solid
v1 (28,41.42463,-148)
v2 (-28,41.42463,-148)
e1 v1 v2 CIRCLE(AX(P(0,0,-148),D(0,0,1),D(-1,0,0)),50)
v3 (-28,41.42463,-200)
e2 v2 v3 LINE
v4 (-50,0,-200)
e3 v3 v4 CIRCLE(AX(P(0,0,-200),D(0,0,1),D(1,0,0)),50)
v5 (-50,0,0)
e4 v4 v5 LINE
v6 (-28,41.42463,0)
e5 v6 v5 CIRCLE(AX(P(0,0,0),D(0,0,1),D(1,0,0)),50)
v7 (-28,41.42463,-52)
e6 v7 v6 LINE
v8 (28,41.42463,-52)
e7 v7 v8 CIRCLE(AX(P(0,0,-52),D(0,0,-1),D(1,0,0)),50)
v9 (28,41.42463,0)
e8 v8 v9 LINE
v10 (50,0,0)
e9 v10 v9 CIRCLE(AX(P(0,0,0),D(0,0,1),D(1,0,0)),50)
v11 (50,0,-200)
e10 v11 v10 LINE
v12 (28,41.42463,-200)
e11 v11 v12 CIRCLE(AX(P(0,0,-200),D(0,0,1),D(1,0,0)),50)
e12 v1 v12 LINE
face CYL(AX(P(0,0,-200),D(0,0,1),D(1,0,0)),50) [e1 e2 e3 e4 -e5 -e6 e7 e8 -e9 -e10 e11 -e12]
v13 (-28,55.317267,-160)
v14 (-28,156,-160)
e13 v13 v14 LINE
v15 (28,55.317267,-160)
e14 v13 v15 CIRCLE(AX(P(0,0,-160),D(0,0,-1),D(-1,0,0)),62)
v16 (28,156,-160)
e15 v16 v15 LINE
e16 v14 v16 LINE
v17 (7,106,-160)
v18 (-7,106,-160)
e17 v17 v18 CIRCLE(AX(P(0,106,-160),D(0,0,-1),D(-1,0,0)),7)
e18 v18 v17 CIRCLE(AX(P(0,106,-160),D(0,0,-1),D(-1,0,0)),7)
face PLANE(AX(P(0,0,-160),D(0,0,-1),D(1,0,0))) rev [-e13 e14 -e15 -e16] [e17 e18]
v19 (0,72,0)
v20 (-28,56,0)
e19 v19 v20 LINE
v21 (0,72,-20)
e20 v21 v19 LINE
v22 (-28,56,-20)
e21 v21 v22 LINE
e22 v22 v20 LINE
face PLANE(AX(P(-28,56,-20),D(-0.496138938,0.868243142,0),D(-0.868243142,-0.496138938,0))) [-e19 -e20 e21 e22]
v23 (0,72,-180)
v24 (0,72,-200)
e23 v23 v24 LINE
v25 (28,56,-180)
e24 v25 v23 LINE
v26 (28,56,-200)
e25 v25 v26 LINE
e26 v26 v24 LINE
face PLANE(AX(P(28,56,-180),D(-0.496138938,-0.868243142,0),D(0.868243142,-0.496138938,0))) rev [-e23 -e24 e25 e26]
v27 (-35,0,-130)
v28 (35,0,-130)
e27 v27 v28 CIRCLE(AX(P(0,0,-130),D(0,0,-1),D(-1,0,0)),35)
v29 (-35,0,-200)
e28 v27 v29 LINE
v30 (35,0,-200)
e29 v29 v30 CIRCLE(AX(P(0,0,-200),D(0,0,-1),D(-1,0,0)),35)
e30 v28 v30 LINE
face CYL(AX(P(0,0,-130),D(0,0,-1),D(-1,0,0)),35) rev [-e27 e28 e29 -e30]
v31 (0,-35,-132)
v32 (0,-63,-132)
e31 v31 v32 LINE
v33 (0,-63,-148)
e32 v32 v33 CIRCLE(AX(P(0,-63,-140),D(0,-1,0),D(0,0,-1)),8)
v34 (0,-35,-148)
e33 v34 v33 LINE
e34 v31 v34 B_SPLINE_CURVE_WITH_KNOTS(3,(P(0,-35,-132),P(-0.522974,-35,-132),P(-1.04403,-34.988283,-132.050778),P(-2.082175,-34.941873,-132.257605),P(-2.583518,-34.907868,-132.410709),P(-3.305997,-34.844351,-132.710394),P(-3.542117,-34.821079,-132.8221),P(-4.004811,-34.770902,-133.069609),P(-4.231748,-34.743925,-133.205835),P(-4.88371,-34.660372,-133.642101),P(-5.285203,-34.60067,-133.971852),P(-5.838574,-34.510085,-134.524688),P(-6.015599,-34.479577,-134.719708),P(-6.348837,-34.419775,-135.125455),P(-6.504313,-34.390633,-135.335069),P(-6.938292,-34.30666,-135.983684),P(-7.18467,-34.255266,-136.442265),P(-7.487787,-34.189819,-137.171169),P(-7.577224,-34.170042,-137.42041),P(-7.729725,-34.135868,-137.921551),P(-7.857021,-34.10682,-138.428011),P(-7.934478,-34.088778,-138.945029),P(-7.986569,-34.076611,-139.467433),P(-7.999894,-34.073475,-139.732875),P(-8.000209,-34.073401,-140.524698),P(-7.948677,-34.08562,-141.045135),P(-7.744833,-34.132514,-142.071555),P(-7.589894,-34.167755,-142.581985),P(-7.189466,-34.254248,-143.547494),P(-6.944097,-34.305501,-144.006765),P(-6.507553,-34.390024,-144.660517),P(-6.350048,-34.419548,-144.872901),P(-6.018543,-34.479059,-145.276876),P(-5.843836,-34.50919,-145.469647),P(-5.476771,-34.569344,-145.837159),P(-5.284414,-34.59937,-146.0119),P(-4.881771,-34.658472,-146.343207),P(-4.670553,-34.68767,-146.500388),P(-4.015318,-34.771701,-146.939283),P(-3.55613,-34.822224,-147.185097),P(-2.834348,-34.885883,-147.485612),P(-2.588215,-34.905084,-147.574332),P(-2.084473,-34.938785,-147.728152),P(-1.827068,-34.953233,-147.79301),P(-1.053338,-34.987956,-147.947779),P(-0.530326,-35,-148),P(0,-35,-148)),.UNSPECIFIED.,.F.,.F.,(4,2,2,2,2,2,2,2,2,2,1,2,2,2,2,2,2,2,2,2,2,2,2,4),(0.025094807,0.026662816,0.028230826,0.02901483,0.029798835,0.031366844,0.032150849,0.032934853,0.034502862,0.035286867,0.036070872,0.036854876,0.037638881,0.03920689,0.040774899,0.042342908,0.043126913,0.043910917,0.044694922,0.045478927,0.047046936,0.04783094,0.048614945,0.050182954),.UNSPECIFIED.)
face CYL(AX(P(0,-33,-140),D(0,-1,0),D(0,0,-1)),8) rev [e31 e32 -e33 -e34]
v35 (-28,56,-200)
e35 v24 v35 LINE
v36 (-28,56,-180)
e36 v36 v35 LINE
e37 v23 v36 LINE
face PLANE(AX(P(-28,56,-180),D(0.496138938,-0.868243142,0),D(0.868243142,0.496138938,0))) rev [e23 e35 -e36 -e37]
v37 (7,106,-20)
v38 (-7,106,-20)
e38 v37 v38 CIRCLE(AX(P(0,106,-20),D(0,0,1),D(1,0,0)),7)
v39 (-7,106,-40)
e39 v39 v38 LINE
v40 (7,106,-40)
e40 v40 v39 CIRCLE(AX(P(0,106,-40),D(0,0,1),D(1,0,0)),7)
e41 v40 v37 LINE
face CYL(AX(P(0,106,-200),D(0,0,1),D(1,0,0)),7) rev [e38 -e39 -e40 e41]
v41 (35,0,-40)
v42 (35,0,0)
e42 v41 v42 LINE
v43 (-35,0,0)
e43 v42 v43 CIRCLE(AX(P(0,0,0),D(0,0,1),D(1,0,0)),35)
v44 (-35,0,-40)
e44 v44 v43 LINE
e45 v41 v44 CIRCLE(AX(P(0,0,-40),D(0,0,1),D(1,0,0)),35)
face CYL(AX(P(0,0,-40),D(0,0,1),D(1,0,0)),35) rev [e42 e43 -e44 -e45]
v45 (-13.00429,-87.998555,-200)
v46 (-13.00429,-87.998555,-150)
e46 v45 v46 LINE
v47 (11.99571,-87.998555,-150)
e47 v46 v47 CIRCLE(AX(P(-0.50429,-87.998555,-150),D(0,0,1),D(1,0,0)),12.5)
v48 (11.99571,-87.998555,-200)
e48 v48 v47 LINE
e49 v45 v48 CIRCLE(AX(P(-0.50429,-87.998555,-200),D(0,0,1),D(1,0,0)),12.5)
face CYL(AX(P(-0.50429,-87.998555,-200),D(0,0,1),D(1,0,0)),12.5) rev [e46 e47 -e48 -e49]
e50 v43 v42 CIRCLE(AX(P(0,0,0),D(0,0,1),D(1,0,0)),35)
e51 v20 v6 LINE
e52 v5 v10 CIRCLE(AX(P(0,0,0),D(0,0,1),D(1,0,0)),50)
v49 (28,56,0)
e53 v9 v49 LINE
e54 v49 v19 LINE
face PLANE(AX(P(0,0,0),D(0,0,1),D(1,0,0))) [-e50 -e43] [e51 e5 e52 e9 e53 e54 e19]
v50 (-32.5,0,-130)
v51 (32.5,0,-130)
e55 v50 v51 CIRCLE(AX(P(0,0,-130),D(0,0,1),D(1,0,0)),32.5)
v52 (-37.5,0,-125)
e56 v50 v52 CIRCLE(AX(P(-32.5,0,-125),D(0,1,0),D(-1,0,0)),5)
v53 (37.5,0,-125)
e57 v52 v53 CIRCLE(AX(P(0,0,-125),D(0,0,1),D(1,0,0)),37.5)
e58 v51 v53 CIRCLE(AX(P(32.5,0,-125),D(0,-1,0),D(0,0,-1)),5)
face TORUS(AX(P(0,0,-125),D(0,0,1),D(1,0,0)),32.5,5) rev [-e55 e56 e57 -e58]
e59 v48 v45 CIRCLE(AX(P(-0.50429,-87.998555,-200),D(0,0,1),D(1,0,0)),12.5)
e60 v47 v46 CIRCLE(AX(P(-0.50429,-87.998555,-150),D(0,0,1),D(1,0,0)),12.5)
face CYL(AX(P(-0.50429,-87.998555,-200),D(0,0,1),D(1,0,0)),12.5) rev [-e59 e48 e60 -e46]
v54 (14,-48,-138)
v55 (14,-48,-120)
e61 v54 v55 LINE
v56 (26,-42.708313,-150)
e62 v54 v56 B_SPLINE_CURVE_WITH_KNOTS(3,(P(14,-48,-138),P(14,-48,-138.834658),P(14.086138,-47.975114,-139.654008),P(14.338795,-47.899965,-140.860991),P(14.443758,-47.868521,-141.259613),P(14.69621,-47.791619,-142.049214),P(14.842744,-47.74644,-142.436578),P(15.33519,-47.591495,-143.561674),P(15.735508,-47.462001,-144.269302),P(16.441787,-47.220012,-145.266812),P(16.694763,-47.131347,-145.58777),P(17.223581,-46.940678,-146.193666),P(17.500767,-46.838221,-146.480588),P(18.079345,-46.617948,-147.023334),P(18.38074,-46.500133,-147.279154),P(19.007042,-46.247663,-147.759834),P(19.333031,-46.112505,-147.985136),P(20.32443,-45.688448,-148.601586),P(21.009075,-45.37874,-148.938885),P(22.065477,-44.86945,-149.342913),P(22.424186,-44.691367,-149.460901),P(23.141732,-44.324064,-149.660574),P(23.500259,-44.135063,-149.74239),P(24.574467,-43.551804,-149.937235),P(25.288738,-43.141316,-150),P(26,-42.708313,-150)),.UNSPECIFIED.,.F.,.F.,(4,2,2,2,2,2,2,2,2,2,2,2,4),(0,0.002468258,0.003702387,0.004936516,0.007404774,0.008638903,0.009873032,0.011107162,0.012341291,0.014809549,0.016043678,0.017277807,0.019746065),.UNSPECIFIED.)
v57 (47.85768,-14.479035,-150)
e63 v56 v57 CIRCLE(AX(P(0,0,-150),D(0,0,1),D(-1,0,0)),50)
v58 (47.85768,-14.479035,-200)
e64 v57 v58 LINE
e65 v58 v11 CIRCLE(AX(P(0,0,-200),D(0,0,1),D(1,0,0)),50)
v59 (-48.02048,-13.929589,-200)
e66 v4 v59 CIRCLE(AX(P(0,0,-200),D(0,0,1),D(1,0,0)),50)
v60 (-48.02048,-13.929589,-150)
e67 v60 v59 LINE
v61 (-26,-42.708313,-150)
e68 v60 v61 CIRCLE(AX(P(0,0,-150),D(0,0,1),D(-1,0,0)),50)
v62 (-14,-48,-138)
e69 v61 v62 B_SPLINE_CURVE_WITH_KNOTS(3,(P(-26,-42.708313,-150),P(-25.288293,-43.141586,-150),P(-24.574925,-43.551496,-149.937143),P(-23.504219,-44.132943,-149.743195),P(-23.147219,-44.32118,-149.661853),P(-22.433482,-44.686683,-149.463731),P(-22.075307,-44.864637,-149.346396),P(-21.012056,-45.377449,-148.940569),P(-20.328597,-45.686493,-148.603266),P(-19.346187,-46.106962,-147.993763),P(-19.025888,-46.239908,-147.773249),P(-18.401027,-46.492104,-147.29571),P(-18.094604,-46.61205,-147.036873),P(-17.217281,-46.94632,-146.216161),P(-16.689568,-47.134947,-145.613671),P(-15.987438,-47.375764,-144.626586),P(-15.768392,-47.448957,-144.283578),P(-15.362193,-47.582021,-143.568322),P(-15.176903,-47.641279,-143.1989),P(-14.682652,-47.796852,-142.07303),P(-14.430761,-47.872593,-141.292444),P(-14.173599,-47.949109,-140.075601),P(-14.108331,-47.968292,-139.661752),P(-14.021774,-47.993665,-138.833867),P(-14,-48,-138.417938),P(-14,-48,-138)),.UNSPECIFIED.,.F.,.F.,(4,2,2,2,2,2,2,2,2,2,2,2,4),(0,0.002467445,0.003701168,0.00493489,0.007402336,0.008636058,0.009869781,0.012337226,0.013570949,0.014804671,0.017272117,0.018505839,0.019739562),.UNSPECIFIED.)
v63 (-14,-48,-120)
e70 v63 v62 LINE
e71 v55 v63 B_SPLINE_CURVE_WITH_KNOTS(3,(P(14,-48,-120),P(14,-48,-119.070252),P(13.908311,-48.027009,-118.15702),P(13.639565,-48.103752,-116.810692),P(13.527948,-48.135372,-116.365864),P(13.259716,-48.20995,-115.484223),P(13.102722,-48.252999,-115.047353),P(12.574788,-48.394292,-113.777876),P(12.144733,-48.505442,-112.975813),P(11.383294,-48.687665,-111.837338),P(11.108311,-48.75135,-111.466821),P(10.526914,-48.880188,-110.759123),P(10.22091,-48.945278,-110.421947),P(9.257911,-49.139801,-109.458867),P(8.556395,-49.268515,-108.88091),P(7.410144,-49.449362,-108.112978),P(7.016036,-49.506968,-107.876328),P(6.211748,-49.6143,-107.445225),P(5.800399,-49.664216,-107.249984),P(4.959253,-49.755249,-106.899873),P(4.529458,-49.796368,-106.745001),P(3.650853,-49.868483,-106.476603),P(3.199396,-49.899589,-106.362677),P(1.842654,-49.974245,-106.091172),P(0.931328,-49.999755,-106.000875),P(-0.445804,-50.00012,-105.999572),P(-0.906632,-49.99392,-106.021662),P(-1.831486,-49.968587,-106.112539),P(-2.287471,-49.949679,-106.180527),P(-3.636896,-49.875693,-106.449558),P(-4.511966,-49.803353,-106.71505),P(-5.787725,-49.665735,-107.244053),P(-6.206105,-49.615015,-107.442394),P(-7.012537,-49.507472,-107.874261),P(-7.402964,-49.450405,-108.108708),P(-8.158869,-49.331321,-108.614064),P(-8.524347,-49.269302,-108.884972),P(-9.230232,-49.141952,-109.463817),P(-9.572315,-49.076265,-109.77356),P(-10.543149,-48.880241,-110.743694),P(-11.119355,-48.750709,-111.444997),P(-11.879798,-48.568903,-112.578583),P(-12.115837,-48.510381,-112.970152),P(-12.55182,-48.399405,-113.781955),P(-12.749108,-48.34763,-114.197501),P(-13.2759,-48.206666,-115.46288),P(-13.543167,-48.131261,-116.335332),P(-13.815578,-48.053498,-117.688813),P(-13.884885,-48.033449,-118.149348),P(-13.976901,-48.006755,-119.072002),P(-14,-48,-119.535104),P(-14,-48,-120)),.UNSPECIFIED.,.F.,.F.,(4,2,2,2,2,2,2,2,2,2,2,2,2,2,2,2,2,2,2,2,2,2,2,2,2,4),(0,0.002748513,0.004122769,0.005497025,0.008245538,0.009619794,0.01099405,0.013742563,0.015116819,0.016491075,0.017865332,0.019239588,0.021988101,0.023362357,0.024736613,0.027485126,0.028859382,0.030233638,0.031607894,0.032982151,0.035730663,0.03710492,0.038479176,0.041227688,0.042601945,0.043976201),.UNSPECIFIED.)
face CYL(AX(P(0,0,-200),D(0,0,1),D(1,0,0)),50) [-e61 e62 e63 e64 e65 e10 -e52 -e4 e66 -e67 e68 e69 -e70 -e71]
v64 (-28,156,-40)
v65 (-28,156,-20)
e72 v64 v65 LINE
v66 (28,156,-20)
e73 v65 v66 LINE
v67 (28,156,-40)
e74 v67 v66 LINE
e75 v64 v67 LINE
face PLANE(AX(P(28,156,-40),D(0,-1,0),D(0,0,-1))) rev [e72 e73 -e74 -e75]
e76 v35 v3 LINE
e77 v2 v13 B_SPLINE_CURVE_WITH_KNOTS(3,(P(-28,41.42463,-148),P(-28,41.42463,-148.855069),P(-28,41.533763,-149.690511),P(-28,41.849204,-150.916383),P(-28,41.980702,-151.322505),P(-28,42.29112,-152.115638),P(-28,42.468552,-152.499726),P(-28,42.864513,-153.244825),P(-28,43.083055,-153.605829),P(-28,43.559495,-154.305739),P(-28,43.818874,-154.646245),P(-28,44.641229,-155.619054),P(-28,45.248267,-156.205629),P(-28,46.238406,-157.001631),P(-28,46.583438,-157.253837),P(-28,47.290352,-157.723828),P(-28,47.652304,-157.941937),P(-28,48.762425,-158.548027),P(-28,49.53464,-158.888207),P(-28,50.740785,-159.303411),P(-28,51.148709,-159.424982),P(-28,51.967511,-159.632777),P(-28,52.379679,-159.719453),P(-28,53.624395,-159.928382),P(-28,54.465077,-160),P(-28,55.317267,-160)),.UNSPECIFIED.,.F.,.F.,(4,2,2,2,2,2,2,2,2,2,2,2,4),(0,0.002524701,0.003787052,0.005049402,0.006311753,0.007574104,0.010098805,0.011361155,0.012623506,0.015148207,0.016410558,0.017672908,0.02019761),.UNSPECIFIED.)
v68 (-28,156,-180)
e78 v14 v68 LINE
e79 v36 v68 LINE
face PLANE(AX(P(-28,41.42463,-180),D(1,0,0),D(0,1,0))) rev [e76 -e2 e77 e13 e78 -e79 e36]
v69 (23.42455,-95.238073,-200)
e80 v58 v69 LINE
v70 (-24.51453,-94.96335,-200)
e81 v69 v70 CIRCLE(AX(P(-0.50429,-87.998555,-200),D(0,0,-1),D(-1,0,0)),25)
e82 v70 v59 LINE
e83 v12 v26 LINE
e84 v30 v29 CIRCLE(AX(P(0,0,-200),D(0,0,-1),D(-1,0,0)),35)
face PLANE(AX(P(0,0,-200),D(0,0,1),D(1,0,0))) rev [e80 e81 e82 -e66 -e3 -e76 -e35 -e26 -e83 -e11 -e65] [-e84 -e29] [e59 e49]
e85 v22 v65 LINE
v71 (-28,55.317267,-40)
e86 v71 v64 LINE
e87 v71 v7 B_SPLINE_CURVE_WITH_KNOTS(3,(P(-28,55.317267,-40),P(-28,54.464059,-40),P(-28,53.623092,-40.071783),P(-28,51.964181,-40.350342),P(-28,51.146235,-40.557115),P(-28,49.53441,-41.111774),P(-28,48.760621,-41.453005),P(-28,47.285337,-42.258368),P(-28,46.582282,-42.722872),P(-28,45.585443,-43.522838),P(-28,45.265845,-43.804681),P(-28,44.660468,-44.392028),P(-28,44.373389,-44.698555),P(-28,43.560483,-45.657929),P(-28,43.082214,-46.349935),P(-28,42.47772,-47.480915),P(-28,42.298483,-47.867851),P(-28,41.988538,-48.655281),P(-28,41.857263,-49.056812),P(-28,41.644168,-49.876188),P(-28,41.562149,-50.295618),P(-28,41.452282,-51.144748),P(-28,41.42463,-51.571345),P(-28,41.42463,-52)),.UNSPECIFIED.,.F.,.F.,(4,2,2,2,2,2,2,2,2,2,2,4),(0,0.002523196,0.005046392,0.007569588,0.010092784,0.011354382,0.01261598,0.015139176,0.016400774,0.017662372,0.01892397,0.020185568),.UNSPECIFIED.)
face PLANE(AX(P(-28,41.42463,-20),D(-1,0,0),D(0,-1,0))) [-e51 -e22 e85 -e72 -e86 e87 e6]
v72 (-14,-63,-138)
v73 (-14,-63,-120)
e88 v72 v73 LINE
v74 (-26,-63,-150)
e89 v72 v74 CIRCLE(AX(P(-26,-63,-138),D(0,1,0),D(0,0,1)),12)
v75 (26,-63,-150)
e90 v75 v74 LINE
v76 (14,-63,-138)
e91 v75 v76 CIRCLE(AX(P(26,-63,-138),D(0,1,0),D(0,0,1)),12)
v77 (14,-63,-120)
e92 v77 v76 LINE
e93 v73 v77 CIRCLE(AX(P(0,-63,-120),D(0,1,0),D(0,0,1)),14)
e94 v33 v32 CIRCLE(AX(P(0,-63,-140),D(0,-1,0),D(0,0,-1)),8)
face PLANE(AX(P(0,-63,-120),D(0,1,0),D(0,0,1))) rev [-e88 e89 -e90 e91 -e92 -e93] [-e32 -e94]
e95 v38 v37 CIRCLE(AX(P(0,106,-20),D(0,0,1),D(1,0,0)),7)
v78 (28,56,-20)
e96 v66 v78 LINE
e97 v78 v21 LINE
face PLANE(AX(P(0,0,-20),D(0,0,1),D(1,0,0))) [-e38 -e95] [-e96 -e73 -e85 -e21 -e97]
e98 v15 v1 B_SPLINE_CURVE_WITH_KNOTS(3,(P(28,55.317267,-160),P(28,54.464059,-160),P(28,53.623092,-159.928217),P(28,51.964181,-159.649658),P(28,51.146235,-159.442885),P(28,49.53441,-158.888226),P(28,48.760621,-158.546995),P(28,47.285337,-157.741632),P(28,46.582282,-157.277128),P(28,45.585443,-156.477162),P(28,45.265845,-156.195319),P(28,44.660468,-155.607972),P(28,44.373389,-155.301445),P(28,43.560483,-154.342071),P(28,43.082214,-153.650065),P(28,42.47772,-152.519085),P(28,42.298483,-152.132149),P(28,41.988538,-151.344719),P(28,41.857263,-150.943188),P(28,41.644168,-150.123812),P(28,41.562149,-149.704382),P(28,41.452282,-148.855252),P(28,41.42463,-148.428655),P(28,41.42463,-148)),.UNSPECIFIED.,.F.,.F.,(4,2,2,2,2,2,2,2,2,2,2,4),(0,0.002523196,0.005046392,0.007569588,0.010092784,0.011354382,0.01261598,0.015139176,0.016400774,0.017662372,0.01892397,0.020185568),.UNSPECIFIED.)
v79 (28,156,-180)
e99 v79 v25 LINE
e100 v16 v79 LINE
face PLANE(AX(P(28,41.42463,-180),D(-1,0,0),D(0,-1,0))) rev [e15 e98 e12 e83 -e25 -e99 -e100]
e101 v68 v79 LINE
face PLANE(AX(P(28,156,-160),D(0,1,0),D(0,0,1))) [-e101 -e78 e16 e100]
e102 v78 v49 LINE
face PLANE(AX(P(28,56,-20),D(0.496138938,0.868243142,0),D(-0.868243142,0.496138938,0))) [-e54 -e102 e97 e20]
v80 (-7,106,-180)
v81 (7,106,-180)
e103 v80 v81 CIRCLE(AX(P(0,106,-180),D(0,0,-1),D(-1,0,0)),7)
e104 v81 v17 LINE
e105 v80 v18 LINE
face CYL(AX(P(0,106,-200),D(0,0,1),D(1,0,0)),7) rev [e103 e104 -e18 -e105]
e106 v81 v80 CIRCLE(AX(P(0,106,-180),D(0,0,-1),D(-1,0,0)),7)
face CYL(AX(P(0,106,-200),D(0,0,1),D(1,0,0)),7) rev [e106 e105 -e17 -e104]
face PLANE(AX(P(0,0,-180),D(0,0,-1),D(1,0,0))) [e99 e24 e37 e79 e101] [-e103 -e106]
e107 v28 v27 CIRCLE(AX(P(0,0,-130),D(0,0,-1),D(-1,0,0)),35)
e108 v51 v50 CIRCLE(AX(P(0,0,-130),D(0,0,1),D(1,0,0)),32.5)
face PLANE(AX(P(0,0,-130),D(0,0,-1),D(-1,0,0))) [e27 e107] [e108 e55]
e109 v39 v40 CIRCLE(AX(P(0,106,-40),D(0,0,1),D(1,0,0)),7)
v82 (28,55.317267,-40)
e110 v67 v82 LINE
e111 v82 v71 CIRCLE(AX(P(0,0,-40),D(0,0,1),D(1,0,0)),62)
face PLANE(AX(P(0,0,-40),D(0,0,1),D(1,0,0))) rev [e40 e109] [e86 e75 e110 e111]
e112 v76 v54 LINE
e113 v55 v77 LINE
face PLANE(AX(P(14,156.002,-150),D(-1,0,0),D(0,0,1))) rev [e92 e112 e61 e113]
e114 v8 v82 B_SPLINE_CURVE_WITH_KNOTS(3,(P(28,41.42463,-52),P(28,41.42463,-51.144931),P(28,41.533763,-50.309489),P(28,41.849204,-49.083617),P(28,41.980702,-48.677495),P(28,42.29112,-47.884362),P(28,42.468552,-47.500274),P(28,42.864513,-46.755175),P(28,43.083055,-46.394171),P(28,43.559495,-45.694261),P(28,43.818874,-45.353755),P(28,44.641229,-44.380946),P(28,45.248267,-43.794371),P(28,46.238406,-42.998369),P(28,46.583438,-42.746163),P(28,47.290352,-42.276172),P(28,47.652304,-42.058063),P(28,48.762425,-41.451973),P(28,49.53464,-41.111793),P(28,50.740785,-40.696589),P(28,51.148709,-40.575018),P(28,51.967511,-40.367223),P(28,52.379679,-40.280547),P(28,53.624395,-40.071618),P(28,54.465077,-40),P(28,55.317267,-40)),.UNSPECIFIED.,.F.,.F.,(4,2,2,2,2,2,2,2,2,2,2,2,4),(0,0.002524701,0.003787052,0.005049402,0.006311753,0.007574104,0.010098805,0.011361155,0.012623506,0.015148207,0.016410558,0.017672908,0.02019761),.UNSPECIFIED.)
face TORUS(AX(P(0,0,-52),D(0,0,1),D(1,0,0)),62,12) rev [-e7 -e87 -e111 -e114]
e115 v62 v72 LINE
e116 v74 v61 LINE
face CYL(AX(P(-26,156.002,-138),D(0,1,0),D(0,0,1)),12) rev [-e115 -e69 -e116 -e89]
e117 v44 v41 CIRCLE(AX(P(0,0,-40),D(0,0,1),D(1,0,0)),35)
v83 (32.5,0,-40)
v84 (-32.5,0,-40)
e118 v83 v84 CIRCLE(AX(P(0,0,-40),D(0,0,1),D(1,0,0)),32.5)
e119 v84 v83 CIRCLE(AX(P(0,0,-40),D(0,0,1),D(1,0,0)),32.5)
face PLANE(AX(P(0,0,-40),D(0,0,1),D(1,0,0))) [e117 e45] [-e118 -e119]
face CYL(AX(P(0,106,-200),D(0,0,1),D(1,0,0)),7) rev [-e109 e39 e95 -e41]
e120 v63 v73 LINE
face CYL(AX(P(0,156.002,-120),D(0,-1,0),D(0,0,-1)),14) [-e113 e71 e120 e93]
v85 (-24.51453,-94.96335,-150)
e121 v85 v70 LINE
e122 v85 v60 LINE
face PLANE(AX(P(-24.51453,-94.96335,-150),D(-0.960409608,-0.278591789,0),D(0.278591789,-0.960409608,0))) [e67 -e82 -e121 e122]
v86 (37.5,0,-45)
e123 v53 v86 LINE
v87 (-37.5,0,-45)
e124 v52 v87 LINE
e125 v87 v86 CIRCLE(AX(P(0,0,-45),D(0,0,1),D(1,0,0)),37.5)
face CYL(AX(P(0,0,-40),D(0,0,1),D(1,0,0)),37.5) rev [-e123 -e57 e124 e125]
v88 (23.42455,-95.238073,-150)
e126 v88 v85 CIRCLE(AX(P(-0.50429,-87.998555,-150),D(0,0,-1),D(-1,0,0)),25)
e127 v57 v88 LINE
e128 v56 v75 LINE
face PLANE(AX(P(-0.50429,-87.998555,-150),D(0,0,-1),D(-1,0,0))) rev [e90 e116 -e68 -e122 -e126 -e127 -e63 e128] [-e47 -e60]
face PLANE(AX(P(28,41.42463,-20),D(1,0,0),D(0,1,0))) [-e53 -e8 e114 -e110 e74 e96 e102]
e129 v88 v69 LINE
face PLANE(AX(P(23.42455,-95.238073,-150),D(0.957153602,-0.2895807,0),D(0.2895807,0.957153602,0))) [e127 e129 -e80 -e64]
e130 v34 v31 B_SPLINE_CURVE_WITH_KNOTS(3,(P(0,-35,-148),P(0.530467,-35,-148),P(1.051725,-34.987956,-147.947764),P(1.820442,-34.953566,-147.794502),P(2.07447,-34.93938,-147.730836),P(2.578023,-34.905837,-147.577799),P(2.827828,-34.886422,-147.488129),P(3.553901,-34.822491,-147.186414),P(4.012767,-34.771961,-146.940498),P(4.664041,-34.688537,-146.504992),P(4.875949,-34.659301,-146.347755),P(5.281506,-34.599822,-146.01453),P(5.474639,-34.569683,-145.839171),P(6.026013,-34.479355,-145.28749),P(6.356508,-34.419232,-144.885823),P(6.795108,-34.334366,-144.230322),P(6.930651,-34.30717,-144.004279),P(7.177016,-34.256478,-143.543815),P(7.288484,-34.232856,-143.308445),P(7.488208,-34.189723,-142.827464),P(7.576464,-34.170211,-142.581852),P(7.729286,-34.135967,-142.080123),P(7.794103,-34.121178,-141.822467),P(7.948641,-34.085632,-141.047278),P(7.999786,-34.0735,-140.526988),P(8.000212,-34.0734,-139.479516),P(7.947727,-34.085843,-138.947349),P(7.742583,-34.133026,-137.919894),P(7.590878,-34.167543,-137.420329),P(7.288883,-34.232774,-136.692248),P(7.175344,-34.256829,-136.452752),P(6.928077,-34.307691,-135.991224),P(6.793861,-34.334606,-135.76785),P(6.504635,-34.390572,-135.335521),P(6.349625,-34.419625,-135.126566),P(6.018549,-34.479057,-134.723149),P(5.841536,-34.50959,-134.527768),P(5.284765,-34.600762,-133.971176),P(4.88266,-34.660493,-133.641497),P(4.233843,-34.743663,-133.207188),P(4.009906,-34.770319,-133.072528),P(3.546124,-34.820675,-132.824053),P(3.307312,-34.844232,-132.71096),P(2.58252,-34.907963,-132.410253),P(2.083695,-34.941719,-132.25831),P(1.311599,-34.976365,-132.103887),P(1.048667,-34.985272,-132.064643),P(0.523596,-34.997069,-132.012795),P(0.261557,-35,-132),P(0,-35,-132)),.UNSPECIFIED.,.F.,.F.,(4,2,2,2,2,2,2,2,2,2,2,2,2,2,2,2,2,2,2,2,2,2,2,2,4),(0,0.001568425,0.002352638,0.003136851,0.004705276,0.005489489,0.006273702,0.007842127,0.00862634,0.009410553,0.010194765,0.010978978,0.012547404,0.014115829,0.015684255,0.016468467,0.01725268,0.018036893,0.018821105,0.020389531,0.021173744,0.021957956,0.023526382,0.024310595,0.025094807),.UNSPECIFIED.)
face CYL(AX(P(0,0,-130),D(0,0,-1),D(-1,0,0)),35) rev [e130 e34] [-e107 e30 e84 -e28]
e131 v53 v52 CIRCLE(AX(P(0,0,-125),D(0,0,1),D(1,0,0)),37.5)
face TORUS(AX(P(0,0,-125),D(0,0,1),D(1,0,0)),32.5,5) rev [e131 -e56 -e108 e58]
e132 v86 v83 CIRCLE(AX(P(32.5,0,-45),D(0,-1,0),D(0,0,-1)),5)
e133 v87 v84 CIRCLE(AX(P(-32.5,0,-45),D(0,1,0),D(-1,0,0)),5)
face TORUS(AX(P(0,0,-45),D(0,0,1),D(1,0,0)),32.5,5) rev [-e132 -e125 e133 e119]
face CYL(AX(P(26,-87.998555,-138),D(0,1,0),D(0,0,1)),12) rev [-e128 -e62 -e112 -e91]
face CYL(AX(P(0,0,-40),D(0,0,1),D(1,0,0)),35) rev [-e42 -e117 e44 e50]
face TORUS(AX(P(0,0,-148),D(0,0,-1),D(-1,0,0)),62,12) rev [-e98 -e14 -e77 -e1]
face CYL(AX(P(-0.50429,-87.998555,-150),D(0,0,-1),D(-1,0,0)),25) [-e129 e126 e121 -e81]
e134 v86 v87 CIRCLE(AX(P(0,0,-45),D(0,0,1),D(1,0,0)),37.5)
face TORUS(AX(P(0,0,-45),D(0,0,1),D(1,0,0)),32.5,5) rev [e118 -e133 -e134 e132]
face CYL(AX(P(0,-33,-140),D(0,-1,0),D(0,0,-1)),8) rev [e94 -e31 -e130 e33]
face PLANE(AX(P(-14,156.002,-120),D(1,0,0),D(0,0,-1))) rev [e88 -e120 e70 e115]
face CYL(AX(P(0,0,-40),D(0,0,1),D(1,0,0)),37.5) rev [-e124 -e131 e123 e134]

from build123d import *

# Parameters (mm, degrees)
BARREL_PROFILE_100_R       = 50
BARREL_100X200_DEPTH       = 200
FRONT_BORE_PROFILE_70_R    = 35
FRONT_BORE_70X40_DEPTH     = 40
BORE_START                 = -70
BORE_EXTENSION_PROFILE_R   = 35
BORE_EXTENSION_70X70_DEPTH = 70
EAR_PAD_DEPTH              = 20
MOUNTING_EAR_DEPTH         = 20
BASE_START                 = -50
BASE_BLOCK_DEPTH           = 50
BASE_HOLE_PROFILE_25_R     = 12.5
BASE_HOLE_25_DEPTH         = 50
BASE_BRACKET_REACH         = 302.767
BASE_BRACKET_END_RADIUS    = 50
BRACKET_HOLE_PROFILE_16_R  = 8
BRACKET_HOLE_16_DEPTH      = 30
BRACKET_FILLET_R12_R       = 12
EAR_PIN_HOLE_PROFILE_14_R  = 7
EAR_PIN_HOLES_14_DEPTH     = 244.384469607
EAR_FILLETS_R12_R          = 12


with BuildPart() as part:
    # Barrel Profile Ø100 → Barrel Ø100x200 (new body)
    with BuildSketch(Plane.XY):
        Circle(BARREL_PROFILE_100_R)
    extrude(amount=-BARREL_100X200_DEPTH)

    # Front Bore Profile Ø70 → Front Bore Ø70x40 (cut)
    with BuildSketch(Plane.XY):
        Circle(FRONT_BORE_PROFILE_70_R)
    extrude(amount=-FRONT_BORE_70X40_DEPTH, mode=Mode.SUBTRACT)

    # Bore Extension Profile → Bore Extension Ø70x70 (cut)
    with BuildSketch(Plane(origin=(0, 0, -200), x_dir=(-1, 0, 0), z_dir=(0, 0, -1)).offset(BORE_START)):
        with Locations(Location((0, 0, 0), (0, 0, 180))):
            Circle(BORE_EXTENSION_PROFILE_R)
    extrude(amount=BORE_EXTENSION_70X70_DEPTH, mode=Mode.SUBTRACT)

    # Ear Pad Profile → Ear Pad (add)
    with BuildSketch(Plane.XY):
        with BuildLine():
            Line((-28, 41.424630354), (-28, 56))
            Line((-28, 56), (0, 72))
            Line((0, 72), (28, 56))
            Line((28, 56), (28, 41.424630354))
            ThreePointArc((28, 41.424630354), (0, 50), (-28, 41.424630354))
        make_face()
    ear_pad = extrude(amount=-EAR_PAD_DEPTH)

    # Ear Profile → Mounting Ear (add)
    with BuildSketch(Plane(origin=(0, 0, -20), x_dir=(-1, 0, 0), z_dir=(0, 0, -1))):
        with BuildLine():
            Line((-28, 41.424630354), (-28, 56))
            Line((-28, 56), (-28, 156))
            Line((-28, 156), (28, 156))
            Line((28, 156), (28, 41.424630354))
            ThreePointArc((28, 41.424630354), (0, 50), (-28, 41.424630354))
        make_face()
    mounting_ear = extrude(amount=MOUNTING_EAR_DEPTH)

    # Ear Mirror: Ear Pad, Mounting Ear across plane
    add(ear_pad.mirror(Plane.XY.offset(-100)))
    add(mounting_ear.mirror(Plane.XY.offset(-100)))

    # Bore Groove Profile → Bore Groove (revolve, cut)
    with BuildSketch(Plane(origin=(0, 0, 0), x_dir=(0, 0, -1), z_dir=(1, 0, 0)), mode=Mode.PRIVATE) as bore_groove_sk:
        with BuildLine():
            Line((40, 0), (40, 32.5))
            ThreePointArc((40, 32.5), (41.464466094, 36.035533906), (45, 37.5))
            Line((45, 37.5), (125, 37.5))
            ThreePointArc((125, 37.5), (128.535533906, 36.035533906), (130, 32.5))
            Line((130, 32.5), (130, 0))
            Line((130, 0), (40, 0))
        make_face()
    revolve(bore_groove_sk.sketch.rotate(Axis((0, 0, -40), (0, 0, -1)), 90), axis=Axis((0, 0, -40), (0, 0, -1)), mode=Mode.SUBTRACT)

    # Base Block Profile → Base Block (add)
    with BuildSketch(Plane(origin=(0, 0, -200), x_dir=(-1, 0, 0), z_dir=(0, 0, -1)).offset(BASE_START)):
        with BuildLine():
            Line((-23.424549882, -95.238072549), (-47.857680112, -14.479034992))
            ThreePointArc((-47.857680112, -14.479034992), (0.286528508, -49.999179007), (48.020480401, -13.929589444))
            Line((48.020480401, -13.929589444), (24.514530374, -94.963349775))
            ThreePointArc((24.514530374, -94.963349775), (0.647554428, -112.998144557), (-23.424549882, -95.238072549))
        make_face()
    extrude(amount=BASE_BLOCK_DEPTH)

    # Base Hole Profile Ø25 → Base Hole Ø25 (cut)
    with BuildSketch(Plane.XY.offset(-150)):
        with Locations((-0.504290174, -87.998555053)):
            Circle(BASE_HOLE_PROFILE_25_R)
    extrude(amount=-BASE_HOLE_25_DEPTH, mode=Mode.SUBTRACT)

    # Base Bracket: up to this cylinder (the profile starts outside it)
    base_bracket_end = Plane(origin=(0, 0, -129.383127), z_dir=(0, 0, 1)) * Cylinder(BASE_BRACKET_END_RADIUS, 706.534, mode=Mode.PRIVATE)
    # Base Bracket Profile → Base Bracket (add, up to the surface)
    with BuildSketch(Plane(origin=(0, -63, 0), x_dir=(1, 0, 0), z_dir=(0, 1, 0)), mode=Mode.PRIVATE) as base_bracket_sk1:
        with BuildLine():
            Line((-14, 120), (-14, 150))
            Line((-14, 150), (14, 150))
            Line((14, 150), (14, 120))
            ThreePointArc((14, 120), (0, 106), (-14, 120))
        make_face()
    base_bracket_tool1 = extrude(base_bracket_sk1.sketch, amount=BASE_BRACKET_REACH, mode=Mode.PRIVATE) - base_bracket_end
    add(base_bracket_tool1.solids().sort_by_distance((0, -63, -129.383127))[0])

    # Bracket Hole Profile Ø16 → Bracket Hole Ø16 (cut)
    with BuildSketch(Plane.XZ.offset(63)):
        with Locations(Location((0, -140, 0), (0, 0, 270))):
            Circle(BRACKET_HOLE_PROFILE_16_R)
    extrude(amount=-BRACKET_HOLE_16_DEPTH, mode=Mode.SUBTRACT)

    # Bracket Fillet R12
    bracket_fillet_r12_edges = [part.edges().sort_by_distance(p)[0] for p in [
        (-14, -55.5, -150),
        (14, -55.5, -150),
    ]]
    fillet(bracket_fillet_r12_edges, radius=BRACKET_FILLET_R12_R)

    # Ear Pin Hole Profile Ø14 → Ear Pin Holes Ø14 (cut, through all)
    with BuildSketch(Plane.XY.offset(-20)):
        with Locations((0, 106)):
            Circle(EAR_PIN_HOLE_PROFILE_14_R)
    extrude(amount=-EAR_PIN_HOLES_14_DEPTH, mode=Mode.SUBTRACT)

    # Ear Fillets R12
    ear_fillets_r12_edges = [part.edges().sort_by_distance(p)[0] for p in [
        (0, 50, -40),
        (0, 50, -160),
    ]]
    fillet(ear_fillets_r12_edges, radius=EAR_FILLETS_R12_R)


solid = part.part
